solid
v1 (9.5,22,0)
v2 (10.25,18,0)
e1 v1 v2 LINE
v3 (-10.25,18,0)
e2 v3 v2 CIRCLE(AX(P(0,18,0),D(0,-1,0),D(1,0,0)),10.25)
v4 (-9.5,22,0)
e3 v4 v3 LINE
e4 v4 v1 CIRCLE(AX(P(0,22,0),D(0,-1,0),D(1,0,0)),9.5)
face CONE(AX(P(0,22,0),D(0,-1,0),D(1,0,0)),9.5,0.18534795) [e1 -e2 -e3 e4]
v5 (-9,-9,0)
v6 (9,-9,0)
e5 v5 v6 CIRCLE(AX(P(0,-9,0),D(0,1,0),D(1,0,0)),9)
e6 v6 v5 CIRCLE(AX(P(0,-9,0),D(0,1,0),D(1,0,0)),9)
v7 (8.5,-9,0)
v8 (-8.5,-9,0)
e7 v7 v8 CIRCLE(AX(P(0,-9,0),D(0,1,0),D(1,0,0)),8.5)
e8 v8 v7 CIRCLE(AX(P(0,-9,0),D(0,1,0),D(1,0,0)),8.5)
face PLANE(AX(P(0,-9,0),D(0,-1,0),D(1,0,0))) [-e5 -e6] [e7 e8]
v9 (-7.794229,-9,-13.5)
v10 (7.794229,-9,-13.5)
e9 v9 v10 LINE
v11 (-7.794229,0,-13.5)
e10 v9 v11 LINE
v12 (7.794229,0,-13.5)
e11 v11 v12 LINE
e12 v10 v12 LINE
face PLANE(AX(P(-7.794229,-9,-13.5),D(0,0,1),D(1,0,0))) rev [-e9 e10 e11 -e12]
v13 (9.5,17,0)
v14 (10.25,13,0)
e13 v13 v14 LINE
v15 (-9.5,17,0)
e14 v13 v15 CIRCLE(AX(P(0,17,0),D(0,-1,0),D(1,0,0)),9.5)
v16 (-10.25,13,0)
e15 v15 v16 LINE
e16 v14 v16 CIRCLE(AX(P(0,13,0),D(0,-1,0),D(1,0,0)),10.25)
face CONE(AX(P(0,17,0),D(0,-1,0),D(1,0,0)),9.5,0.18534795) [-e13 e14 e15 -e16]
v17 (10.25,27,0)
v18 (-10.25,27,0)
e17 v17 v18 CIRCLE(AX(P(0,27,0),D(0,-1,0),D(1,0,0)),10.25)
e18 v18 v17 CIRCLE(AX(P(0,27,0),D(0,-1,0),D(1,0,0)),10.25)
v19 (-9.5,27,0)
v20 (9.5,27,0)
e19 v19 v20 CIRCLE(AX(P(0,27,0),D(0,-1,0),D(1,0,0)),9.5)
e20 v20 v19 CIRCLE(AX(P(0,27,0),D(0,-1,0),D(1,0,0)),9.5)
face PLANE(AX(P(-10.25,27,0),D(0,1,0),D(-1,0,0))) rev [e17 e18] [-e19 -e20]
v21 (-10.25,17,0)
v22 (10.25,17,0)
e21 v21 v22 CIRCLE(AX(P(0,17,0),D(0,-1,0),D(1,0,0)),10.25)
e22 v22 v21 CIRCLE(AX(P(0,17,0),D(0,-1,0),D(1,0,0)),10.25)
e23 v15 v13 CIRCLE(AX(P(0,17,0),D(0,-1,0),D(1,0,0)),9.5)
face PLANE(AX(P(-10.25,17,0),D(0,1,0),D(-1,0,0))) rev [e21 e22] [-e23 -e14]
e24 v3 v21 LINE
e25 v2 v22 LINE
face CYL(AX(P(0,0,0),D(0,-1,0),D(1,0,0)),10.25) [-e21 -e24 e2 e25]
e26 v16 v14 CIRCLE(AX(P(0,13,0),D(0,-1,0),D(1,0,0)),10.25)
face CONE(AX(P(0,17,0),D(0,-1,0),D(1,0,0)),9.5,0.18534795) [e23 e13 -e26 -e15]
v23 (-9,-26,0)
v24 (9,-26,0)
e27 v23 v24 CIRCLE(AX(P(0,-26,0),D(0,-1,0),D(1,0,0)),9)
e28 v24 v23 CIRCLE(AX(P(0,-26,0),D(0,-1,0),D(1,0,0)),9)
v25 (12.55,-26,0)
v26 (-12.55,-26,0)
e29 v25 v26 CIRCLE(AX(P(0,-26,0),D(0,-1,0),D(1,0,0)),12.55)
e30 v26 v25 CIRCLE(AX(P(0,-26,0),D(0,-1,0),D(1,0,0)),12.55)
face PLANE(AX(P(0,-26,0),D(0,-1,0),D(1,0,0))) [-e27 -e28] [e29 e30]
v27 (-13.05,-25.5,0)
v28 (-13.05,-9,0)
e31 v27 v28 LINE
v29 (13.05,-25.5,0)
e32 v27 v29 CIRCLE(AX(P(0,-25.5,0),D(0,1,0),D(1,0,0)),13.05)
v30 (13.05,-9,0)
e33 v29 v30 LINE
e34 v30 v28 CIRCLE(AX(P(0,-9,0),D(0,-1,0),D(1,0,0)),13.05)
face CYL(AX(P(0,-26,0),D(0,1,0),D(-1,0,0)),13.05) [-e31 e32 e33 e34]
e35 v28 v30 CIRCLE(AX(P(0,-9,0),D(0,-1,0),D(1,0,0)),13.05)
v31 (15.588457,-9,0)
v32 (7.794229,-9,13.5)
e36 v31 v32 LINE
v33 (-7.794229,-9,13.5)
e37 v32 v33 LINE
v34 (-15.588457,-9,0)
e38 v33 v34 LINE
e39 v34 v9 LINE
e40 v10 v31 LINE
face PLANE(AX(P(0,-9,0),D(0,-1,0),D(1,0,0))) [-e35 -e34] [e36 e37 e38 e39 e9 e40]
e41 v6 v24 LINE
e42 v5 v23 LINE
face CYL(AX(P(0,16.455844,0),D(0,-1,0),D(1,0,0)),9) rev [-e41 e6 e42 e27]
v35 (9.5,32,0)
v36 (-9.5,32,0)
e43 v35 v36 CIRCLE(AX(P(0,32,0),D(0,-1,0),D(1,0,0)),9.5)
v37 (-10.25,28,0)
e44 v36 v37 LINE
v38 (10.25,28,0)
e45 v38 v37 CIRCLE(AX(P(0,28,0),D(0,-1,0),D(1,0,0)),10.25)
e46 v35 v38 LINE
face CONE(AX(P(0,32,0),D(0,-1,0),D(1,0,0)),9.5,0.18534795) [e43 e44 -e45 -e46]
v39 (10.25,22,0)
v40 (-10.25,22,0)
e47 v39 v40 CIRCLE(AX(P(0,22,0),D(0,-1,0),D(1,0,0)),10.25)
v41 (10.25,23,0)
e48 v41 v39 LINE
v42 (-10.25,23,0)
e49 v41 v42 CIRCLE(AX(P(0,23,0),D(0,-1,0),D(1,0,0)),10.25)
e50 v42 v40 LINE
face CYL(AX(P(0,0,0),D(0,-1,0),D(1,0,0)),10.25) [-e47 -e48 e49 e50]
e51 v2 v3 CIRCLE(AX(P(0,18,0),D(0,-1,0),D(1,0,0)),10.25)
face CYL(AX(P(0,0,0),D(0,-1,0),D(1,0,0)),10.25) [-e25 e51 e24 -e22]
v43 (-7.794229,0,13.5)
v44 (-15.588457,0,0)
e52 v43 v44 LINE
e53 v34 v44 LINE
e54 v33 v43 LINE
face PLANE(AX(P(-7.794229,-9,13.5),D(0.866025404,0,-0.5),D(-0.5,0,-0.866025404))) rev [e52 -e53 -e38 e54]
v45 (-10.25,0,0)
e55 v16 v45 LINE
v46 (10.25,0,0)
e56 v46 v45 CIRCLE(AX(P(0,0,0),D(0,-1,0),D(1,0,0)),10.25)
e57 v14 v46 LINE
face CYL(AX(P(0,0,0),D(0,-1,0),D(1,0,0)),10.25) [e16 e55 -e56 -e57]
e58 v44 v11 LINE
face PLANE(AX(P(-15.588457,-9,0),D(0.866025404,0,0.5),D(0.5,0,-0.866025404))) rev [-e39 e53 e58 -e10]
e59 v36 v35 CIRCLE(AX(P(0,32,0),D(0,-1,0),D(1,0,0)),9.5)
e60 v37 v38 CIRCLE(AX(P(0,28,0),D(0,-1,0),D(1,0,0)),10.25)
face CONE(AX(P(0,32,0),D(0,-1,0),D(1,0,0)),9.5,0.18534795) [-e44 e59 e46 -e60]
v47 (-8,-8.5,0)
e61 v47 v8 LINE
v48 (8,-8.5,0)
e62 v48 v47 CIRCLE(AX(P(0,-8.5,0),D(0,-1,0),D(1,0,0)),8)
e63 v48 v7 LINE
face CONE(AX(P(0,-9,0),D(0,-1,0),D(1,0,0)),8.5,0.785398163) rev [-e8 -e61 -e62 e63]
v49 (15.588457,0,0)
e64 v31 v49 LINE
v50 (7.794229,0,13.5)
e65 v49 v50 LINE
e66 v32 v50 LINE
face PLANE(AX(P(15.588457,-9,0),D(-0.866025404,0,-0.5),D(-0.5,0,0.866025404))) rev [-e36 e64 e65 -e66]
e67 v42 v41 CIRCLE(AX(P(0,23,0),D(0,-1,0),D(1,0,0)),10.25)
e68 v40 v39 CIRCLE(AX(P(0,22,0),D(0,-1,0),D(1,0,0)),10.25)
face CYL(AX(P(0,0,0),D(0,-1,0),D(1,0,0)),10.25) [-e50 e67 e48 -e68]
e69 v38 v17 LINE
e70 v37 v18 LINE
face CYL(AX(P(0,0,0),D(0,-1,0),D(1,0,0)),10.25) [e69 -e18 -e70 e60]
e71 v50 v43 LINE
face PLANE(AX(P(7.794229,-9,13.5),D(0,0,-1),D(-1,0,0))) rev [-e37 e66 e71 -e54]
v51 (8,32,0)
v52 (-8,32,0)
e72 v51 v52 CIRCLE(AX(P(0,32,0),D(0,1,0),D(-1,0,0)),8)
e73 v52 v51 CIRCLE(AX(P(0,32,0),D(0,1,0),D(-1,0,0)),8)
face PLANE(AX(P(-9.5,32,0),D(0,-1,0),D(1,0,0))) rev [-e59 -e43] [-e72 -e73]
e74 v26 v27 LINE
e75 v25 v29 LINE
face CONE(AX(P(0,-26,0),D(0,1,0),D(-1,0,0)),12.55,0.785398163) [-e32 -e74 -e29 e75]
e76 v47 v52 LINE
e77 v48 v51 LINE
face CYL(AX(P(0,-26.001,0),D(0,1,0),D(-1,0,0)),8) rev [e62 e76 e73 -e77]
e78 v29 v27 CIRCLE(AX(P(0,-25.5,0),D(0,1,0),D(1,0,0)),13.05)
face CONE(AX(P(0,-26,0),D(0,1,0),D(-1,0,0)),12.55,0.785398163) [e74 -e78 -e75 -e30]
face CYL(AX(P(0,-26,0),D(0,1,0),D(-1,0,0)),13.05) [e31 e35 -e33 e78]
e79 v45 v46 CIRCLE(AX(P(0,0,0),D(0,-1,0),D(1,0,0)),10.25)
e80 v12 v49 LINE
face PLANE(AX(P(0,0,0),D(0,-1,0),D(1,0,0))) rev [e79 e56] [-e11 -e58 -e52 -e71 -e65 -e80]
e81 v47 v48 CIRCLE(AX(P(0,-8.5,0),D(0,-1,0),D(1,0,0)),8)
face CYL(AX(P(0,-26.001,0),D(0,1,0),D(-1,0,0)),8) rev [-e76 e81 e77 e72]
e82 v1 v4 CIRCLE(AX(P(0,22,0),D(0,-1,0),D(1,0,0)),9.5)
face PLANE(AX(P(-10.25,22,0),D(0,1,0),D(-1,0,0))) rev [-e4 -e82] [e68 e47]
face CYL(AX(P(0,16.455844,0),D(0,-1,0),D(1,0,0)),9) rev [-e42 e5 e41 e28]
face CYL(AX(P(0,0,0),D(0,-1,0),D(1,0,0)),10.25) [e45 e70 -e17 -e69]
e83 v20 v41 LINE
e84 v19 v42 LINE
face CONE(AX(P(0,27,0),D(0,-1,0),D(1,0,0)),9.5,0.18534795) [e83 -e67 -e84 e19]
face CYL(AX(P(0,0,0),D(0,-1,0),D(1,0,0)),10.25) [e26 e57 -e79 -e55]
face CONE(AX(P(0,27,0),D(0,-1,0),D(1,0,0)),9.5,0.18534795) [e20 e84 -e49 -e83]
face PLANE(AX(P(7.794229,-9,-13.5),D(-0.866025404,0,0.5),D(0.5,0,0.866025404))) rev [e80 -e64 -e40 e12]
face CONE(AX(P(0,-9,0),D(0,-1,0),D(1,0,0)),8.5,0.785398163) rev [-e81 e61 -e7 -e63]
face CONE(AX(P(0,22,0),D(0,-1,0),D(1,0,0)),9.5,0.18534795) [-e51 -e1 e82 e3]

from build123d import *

# Parameters (mm, degrees)
EXTRUDE_1_DEPTH     = 9
SKETCH_3_R          = 13.05
EXTRUDE_2_DEPTH     = 17
CUT_EXTRUDE_1_REACH = 63.557
SKETCH_4_R          = 8
SKETCH_5_R          = 9
CUT_EXTRUDE_2_DEPTH = 17
CHAMFER_1_SIZE      = 0.5
CHAMFER_2_SIZE      = 0.5


with BuildPart() as part:
    # 草图1 → 旋转1 (revolve)
    with BuildSketch(Plane.XY, mode=Mode.PRIVATE) as revolve_1_sk:
        Polygon((-10.25, 13), (-9.5, 17), (-10.25, 17), (-10.25, 18), (-9.5, 22), (-10.25, 22), (-10.25, 23), (-9.5, 27), (-10.25, 27), (-10.25, 28), (-9.5, 32), (0, 32), (0, 0), (-10.25, 0), align=None)
    revolve(revolve_1_sk.sketch.rotate(Axis((0, 0, 0), (0, 1, 0)), 180), axis=Axis((0, 0, 0), (0, 1, 0)))

    # 草图2 → 凸台-拉伸1 (add)
    with BuildSketch(Plane.XZ):
        Polygon((15.588457268, 0), (7.794228634, 13.5), (-7.794228634, 13.5), (-15.588457268, 0), (-7.794228634, -13.5), (7.794228634, -13.5), align=None)
    extrude(amount=EXTRUDE_1_DEPTH)

    # 草图3 → 凸台-拉伸2 (add)
    with BuildSketch(Plane.XZ.offset(9)):
        Circle(SKETCH_3_R)
    extrude(amount=EXTRUDE_2_DEPTH)

    # 草图4 → 切除-拉伸1 (cut, up to next)
    with BuildSketch(Plane(origin=(0, 32, 0), x_dir=(1, 0, 0), z_dir=(0, 1, 0)), mode=Mode.PRIVATE) as cut_extrude_1_sk1:
        with Locations(Location((0, 0, 0), (0, 0, 180))):
            Circle(SKETCH_4_R)
    cut_extrude_1_tool1 = extrude(cut_extrude_1_sk1.sketch, amount=-CUT_EXTRUDE_1_REACH, mode=Mode.PRIVATE) & part.part
    add(cut_extrude_1_tool1.solids().sort_by_distance((0, 32, 0))[0], mode=Mode.SUBTRACT)

    # 草图5 → 切除-拉伸2 (cut)
    with BuildSketch(Plane.XZ.offset(26)):
        Circle(SKETCH_5_R)
    extrude(amount=-CUT_EXTRUDE_2_DEPTH, mode=Mode.SUBTRACT)

    # 倒角1
    chamfer_1_edges = [part.edges().sort_by_distance(p)[0] for p in [
        (-13.05, -26, 0),
    ]]
    chamfer(chamfer_1_edges, length=CHAMFER_1_SIZE)

    # 倒角2
    chamfer_2_edges = [part.edges().sort_by_distance(p)[0] for p in [
        (8, -9, 0),
    ]]
    chamfer(chamfer_2_edges, length=CHAMFER_2_SIZE)


solid = part.part
